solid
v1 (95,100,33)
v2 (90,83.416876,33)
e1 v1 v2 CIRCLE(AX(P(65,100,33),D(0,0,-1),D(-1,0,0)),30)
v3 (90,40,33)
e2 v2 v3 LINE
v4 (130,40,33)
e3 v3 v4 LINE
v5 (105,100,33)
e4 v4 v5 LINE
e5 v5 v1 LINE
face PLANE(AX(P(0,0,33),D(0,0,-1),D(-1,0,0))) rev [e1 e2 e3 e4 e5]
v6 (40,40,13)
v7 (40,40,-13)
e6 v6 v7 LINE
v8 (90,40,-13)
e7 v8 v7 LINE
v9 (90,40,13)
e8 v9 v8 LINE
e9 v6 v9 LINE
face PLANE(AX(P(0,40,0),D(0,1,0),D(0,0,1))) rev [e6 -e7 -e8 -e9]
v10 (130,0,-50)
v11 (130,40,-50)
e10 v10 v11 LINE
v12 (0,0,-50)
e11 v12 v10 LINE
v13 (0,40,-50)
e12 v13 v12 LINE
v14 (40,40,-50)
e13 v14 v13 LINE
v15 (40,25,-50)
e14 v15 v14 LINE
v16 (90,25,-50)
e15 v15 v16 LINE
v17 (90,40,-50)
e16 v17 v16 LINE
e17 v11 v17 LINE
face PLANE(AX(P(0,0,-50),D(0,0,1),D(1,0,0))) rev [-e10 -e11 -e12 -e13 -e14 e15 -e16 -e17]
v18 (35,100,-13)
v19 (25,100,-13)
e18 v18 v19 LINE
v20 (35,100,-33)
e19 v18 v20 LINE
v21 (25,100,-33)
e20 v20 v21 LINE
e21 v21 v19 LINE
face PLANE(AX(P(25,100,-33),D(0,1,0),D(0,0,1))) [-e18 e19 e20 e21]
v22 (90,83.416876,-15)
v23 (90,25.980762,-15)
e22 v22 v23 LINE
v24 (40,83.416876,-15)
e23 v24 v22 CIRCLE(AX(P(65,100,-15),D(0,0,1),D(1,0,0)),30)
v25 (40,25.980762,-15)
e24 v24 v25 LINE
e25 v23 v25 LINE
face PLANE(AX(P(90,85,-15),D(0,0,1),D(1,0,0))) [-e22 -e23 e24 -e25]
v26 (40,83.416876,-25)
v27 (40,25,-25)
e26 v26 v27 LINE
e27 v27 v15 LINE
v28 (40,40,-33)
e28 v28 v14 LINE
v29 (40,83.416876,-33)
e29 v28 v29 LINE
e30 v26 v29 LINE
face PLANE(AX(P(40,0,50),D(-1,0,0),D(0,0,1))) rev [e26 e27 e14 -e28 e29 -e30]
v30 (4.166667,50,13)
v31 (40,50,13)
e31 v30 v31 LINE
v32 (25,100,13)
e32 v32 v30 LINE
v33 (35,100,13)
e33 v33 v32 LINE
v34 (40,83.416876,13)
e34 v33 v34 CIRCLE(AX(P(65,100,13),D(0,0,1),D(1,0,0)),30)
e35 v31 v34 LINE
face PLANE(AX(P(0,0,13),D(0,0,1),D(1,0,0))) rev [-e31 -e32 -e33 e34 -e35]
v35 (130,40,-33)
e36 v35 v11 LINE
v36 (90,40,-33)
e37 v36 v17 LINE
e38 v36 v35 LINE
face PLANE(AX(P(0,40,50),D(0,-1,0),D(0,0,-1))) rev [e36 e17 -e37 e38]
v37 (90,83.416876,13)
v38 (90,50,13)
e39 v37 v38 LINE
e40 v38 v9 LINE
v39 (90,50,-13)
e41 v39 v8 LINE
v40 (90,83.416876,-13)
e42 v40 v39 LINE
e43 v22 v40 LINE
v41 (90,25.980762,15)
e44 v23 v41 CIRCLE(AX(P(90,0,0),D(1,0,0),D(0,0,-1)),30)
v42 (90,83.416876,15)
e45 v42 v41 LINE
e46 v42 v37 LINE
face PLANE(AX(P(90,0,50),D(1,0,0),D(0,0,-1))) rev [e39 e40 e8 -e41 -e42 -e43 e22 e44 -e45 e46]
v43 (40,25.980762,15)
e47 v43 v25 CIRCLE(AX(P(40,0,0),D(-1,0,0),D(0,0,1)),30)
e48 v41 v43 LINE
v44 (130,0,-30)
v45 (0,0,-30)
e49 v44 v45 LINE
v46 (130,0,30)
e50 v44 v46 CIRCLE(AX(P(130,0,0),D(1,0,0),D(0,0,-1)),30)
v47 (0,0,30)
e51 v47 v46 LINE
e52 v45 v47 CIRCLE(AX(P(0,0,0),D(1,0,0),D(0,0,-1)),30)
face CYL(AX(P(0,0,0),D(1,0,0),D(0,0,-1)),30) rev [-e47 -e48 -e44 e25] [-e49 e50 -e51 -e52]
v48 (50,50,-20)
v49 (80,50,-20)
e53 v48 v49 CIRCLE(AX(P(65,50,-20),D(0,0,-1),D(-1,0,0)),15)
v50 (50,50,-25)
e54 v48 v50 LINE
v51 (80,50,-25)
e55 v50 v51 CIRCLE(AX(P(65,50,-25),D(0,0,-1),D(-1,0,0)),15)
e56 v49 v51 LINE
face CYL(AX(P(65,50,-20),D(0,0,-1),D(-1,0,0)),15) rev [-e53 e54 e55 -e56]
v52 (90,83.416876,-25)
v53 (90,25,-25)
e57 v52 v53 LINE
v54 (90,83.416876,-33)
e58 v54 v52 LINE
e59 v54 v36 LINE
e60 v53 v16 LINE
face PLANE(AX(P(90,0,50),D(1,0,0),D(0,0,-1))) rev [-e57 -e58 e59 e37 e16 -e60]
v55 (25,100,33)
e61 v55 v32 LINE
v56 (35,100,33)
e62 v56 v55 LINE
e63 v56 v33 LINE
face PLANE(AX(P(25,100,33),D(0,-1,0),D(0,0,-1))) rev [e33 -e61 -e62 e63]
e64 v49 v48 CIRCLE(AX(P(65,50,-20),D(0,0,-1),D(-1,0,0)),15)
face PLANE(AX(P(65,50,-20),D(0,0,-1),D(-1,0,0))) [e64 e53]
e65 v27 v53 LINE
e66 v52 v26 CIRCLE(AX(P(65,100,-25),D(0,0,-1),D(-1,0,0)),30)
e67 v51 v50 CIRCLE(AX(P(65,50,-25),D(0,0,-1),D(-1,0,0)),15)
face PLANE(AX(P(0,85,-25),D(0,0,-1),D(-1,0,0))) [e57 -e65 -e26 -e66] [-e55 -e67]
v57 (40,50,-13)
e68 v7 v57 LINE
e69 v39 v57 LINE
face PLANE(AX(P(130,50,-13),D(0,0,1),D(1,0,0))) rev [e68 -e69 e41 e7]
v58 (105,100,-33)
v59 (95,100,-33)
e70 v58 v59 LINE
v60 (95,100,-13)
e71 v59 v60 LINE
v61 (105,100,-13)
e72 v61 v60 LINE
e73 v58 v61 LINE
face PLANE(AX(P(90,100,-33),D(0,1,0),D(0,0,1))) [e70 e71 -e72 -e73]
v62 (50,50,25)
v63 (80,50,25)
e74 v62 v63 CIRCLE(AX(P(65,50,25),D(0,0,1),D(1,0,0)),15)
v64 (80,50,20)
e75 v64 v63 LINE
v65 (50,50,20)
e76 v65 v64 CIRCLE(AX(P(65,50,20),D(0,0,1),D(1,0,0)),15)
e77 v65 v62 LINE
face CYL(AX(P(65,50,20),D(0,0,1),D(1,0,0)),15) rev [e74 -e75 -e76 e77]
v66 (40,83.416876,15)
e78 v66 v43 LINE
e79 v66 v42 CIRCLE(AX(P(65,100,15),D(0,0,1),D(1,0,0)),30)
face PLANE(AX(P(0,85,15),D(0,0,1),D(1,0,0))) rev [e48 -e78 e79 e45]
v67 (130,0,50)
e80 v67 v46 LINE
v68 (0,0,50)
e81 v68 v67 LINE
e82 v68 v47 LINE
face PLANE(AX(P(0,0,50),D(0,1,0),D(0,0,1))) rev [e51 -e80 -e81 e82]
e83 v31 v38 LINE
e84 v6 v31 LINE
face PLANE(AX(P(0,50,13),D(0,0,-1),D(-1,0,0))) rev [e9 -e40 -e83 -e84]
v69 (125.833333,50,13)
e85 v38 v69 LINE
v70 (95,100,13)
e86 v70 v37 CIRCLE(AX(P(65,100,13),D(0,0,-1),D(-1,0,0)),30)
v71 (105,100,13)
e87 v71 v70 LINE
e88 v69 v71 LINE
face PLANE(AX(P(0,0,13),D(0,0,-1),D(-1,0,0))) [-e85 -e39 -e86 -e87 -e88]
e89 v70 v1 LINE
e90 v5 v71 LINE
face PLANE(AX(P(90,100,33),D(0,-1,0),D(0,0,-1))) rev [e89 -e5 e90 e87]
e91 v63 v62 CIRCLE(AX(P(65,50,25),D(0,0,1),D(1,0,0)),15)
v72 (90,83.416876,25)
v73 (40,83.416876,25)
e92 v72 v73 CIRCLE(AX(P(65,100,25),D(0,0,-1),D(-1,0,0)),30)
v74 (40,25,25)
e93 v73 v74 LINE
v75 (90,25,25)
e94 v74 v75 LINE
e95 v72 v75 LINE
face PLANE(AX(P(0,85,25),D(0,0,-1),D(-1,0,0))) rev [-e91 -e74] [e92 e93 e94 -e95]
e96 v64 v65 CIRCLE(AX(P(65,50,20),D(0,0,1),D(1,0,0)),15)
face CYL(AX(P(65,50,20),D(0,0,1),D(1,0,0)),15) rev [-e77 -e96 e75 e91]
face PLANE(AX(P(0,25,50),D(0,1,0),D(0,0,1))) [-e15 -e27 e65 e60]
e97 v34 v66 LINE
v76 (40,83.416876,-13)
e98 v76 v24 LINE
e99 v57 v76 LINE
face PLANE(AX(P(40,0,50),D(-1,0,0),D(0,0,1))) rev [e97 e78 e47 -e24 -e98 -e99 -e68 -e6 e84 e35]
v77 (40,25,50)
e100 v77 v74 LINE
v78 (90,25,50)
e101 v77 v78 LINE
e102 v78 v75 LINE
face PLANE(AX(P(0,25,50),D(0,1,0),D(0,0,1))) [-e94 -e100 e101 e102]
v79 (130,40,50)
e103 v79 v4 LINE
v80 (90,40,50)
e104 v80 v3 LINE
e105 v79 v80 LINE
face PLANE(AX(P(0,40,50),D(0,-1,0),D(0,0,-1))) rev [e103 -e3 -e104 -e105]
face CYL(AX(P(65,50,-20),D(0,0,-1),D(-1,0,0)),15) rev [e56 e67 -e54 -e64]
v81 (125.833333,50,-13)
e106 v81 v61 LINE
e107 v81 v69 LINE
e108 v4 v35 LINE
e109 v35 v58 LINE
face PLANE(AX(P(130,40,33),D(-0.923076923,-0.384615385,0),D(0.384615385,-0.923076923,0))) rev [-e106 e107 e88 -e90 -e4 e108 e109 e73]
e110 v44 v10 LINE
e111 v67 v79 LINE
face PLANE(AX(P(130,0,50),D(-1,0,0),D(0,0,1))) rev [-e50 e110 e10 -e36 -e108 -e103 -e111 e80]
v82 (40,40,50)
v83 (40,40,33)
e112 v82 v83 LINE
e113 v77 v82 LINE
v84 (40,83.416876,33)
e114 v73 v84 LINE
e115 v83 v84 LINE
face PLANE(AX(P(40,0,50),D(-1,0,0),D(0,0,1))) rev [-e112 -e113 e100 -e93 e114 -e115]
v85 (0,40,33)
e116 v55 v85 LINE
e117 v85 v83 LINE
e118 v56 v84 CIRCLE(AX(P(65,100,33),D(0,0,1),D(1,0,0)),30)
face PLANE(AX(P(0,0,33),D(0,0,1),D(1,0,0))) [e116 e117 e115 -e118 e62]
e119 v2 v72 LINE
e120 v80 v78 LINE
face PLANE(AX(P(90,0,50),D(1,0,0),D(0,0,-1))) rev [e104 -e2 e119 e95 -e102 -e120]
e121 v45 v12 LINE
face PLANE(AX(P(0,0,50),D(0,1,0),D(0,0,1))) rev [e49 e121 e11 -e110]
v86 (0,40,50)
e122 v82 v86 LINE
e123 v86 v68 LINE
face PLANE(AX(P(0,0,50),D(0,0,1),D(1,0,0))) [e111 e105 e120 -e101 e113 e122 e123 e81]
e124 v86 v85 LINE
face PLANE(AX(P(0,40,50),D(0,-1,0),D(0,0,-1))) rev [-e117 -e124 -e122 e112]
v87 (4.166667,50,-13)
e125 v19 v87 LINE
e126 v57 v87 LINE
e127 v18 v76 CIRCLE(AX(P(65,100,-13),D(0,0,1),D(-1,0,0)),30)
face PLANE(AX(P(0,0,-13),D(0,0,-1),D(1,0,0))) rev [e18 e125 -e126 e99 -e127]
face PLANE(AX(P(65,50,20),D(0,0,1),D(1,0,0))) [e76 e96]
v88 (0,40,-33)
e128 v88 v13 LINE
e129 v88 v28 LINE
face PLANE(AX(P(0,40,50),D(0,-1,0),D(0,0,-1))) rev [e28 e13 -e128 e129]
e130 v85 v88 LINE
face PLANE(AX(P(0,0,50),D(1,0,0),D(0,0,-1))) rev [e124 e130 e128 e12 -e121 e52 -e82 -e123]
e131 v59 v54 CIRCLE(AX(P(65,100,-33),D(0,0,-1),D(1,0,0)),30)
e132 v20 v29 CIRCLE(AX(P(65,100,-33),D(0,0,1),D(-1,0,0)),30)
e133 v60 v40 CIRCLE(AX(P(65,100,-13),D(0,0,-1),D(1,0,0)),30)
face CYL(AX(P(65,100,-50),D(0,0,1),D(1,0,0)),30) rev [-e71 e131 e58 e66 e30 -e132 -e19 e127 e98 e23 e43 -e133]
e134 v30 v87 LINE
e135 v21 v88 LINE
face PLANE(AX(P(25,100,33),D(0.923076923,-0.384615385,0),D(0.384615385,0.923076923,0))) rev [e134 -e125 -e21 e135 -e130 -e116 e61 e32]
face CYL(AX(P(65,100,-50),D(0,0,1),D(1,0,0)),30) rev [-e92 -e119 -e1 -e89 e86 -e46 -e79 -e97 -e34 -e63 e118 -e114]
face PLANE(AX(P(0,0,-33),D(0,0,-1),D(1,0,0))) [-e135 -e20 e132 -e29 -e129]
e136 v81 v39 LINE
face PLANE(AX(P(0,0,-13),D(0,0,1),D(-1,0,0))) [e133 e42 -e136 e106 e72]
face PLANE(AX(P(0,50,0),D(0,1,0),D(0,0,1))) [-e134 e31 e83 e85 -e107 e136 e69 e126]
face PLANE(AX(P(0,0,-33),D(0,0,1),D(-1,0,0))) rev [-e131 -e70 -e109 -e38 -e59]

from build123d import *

# Parameters (mm, degrees)
BASE_BLOCK_100_DEPTH          = 50
BOTTOM_ARCH_CUT_DEPTH         = 145.913767462
LEFT_UPRIGHT_SKETCH_W         = 50
LEFT_UPRIGHT_SKETCH_H         = 1.583123952
LEFT_UPRIGHT_60_DEPTH         = 60
RIGHT_UPRIGHT_60_DEPTH        = 60
LEFT_UPRIGHT_RECESS_SKETCH_R  = 15
LEFT_UPRIGHT_RECESS_5_DEPTH   = 5
RIGHT_START                   = -5
RIGHT_UPRIGHT_RECESS_SKETCH_R = 15
RIGHT_UPRIGHT_RECESS_5_DEPTH  = 5
SIDE_WEB_20_DEPTH             = 20
WEB_SADDLE_SKETCH_R           = 30
WEB_SADDLE_CUT_DEPTH          = 176.695759767
CENTRE_RIB_SKETCH_W           = 130
CENTRE_RIB_SKETCH_H           = 26
CENTRE_RIB_10_DEPTH           = 10
RIB_NOTCH_A_DEPTH             = 176.695759767
RIB_NOTCH_B_DEPTH             = 176.695759767
CROSS_HOLE_SKETCH_R           = 30
CROSS_HOLE_30_DEPTH           = 172.464281995


with BuildPart() as part:
    # Base Profile Sketch → Base Block 100 (new, symmetric)
    with BuildSketch(Plane.XY):
        Polygon((0, 40), (0, 0), (130, 0), (130, 40), (90, 40), (90, 25), (65, 25), (40, 25), (40, 40), align=None)
    base_block_100 = extrude(amount=BASE_BLOCK_100_DEPTH, both=True)

    # Bottom Arch Sketch → Bottom Arch Cut (cut, through all)
    with BuildSketch(Plane(origin=(130, 0, 0), x_dir=(0, 0, -1), z_dir=(1, 0, 0))):
        with BuildLine():
            Line((-30, 0), (30, 0))
            ThreePointArc((30, 0), (0, 30), (-30, 0))
        make_face()
        with BuildLine():
            ThreePointArc((-30, 0), (0, -30), (30, 0))
            Line((30, 0), (-30, 0))
        make_face()
    extrude(amount=-BOTTOM_ARCH_CUT_DEPTH, mode=Mode.SUBTRACT)

    # Left Upright Sketch → Left Upright 60 (add)
    with BuildSketch(Plane(origin=(0, 25, 0), x_dir=(1, 0, 0), z_dir=(0, 1, 0))):
        with Locations((65, -15.791561976)):
            Rectangle(LEFT_UPRIGHT_SKETCH_W, LEFT_UPRIGHT_SKETCH_H)
        Polygon((40, -25), (65, -25), (90, -25), (90, -16.583123952), (40, -16.583123952), align=None)
    extrude(amount=LEFT_UPRIGHT_60_DEPTH)

    # Right Upright Sketch → Right Upright 60 (add)
    with BuildSketch(Plane(origin=(0, 25, 0), x_dir=(1, 0, 0), z_dir=(0, 1, 0))):
        Polygon((90, 25), (65, 25), (40, 25), (40, 15), (90, 15), align=None)
    extrude(amount=RIGHT_UPRIGHT_60_DEPTH)

    # Left Upright Recess Sketch → Left Upright Recess 5 (cut)
    with BuildSketch(Plane.XY.offset(25)):
        with Locations((65, 50)):
            Circle(LEFT_UPRIGHT_RECESS_SKETCH_R)
    extrude(amount=-LEFT_UPRIGHT_RECESS_5_DEPTH, mode=Mode.SUBTRACT)

    # Right Upright Recess Sketch → Right Upright Recess 5 (cut)
    with BuildSketch(Plane(origin=(0, 0, -25), x_dir=(-1, 0, 0), z_dir=(0, 0, -1)).offset(RIGHT_START)):
        with Locations(Location((-65, 50, 0), (0, 0, 180))):
            Circle(RIGHT_UPRIGHT_RECESS_SKETCH_R)
    extrude(amount=RIGHT_UPRIGHT_RECESS_5_DEPTH, mode=Mode.SUBTRACT)

    # Side Web Sketch → Side Web 20 (add)
    with BuildSketch(Plane.XY.offset(13)):
        Polygon((40, 40), (40, 100), (25, 100), (0, 40), align=None)
        Polygon((90, 40), (90, 100), (105, 100), (130, 40), align=None)
    side_web_20 = extrude(amount=SIDE_WEB_20_DEPTH)

    # Web Saddle Sketch → Web Saddle Cut (cut, symmetric)
    with BuildSketch(Plane.XY.offset(13)):
        with Locations((65, 100)):
            Circle(WEB_SADDLE_SKETCH_R)
    web_saddle_cut = extrude(amount=WEB_SADDLE_CUT_DEPTH, both=True, mode=Mode.SUBTRACT)

    # Side Web and Saddle Mirror: Base Block 100, Side Web 20, Web Saddle Cut across plane
    add(base_block_100.mirror(Plane.XY))
    add(side_web_20.mirror(Plane.XY))
    add(web_saddle_cut.mirror(Plane.XY), mode=Mode.SUBTRACT)

    # Centre Rib Sketch → Centre Rib 10 (add)
    with BuildSketch(Plane(origin=(0, 40, 0), x_dir=(1, 0, 0), z_dir=(0, 1, 0))):
        with Locations((65, 0)):
            Rectangle(CENTRE_RIB_SKETCH_W, CENTRE_RIB_SKETCH_H)
    extrude(amount=CENTRE_RIB_10_DEPTH)

    # Rib Notch A Sketch → Rib Notch A (cut, through all)
    with BuildSketch(Plane.XY.offset(13)):
        Polygon((4.166666667, 50), (0, 50), (0, 40), align=None)
    extrude(amount=-RIB_NOTCH_A_DEPTH, mode=Mode.SUBTRACT)

    # Rib Notch B Sketch → Rib Notch B (cut, through all)
    with BuildSketch(Plane.XY.offset(13)):
        Polygon((125.833333333, 50), (130, 40), (130, 50), align=None)
    extrude(amount=-RIB_NOTCH_B_DEPTH, mode=Mode.SUBTRACT)

    # Cross Hole Sketch → Cross Hole Ø30 (cut, through all)
    with BuildSketch(Plane(origin=(130, 0, 0), x_dir=(0, 0, -1), z_dir=(1, 0, 0))):
        Circle(CROSS_HOLE_SKETCH_R)
    extrude(amount=-CROSS_HOLE_30_DEPTH, mode=Mode.SUBTRACT)


solid = part.part
